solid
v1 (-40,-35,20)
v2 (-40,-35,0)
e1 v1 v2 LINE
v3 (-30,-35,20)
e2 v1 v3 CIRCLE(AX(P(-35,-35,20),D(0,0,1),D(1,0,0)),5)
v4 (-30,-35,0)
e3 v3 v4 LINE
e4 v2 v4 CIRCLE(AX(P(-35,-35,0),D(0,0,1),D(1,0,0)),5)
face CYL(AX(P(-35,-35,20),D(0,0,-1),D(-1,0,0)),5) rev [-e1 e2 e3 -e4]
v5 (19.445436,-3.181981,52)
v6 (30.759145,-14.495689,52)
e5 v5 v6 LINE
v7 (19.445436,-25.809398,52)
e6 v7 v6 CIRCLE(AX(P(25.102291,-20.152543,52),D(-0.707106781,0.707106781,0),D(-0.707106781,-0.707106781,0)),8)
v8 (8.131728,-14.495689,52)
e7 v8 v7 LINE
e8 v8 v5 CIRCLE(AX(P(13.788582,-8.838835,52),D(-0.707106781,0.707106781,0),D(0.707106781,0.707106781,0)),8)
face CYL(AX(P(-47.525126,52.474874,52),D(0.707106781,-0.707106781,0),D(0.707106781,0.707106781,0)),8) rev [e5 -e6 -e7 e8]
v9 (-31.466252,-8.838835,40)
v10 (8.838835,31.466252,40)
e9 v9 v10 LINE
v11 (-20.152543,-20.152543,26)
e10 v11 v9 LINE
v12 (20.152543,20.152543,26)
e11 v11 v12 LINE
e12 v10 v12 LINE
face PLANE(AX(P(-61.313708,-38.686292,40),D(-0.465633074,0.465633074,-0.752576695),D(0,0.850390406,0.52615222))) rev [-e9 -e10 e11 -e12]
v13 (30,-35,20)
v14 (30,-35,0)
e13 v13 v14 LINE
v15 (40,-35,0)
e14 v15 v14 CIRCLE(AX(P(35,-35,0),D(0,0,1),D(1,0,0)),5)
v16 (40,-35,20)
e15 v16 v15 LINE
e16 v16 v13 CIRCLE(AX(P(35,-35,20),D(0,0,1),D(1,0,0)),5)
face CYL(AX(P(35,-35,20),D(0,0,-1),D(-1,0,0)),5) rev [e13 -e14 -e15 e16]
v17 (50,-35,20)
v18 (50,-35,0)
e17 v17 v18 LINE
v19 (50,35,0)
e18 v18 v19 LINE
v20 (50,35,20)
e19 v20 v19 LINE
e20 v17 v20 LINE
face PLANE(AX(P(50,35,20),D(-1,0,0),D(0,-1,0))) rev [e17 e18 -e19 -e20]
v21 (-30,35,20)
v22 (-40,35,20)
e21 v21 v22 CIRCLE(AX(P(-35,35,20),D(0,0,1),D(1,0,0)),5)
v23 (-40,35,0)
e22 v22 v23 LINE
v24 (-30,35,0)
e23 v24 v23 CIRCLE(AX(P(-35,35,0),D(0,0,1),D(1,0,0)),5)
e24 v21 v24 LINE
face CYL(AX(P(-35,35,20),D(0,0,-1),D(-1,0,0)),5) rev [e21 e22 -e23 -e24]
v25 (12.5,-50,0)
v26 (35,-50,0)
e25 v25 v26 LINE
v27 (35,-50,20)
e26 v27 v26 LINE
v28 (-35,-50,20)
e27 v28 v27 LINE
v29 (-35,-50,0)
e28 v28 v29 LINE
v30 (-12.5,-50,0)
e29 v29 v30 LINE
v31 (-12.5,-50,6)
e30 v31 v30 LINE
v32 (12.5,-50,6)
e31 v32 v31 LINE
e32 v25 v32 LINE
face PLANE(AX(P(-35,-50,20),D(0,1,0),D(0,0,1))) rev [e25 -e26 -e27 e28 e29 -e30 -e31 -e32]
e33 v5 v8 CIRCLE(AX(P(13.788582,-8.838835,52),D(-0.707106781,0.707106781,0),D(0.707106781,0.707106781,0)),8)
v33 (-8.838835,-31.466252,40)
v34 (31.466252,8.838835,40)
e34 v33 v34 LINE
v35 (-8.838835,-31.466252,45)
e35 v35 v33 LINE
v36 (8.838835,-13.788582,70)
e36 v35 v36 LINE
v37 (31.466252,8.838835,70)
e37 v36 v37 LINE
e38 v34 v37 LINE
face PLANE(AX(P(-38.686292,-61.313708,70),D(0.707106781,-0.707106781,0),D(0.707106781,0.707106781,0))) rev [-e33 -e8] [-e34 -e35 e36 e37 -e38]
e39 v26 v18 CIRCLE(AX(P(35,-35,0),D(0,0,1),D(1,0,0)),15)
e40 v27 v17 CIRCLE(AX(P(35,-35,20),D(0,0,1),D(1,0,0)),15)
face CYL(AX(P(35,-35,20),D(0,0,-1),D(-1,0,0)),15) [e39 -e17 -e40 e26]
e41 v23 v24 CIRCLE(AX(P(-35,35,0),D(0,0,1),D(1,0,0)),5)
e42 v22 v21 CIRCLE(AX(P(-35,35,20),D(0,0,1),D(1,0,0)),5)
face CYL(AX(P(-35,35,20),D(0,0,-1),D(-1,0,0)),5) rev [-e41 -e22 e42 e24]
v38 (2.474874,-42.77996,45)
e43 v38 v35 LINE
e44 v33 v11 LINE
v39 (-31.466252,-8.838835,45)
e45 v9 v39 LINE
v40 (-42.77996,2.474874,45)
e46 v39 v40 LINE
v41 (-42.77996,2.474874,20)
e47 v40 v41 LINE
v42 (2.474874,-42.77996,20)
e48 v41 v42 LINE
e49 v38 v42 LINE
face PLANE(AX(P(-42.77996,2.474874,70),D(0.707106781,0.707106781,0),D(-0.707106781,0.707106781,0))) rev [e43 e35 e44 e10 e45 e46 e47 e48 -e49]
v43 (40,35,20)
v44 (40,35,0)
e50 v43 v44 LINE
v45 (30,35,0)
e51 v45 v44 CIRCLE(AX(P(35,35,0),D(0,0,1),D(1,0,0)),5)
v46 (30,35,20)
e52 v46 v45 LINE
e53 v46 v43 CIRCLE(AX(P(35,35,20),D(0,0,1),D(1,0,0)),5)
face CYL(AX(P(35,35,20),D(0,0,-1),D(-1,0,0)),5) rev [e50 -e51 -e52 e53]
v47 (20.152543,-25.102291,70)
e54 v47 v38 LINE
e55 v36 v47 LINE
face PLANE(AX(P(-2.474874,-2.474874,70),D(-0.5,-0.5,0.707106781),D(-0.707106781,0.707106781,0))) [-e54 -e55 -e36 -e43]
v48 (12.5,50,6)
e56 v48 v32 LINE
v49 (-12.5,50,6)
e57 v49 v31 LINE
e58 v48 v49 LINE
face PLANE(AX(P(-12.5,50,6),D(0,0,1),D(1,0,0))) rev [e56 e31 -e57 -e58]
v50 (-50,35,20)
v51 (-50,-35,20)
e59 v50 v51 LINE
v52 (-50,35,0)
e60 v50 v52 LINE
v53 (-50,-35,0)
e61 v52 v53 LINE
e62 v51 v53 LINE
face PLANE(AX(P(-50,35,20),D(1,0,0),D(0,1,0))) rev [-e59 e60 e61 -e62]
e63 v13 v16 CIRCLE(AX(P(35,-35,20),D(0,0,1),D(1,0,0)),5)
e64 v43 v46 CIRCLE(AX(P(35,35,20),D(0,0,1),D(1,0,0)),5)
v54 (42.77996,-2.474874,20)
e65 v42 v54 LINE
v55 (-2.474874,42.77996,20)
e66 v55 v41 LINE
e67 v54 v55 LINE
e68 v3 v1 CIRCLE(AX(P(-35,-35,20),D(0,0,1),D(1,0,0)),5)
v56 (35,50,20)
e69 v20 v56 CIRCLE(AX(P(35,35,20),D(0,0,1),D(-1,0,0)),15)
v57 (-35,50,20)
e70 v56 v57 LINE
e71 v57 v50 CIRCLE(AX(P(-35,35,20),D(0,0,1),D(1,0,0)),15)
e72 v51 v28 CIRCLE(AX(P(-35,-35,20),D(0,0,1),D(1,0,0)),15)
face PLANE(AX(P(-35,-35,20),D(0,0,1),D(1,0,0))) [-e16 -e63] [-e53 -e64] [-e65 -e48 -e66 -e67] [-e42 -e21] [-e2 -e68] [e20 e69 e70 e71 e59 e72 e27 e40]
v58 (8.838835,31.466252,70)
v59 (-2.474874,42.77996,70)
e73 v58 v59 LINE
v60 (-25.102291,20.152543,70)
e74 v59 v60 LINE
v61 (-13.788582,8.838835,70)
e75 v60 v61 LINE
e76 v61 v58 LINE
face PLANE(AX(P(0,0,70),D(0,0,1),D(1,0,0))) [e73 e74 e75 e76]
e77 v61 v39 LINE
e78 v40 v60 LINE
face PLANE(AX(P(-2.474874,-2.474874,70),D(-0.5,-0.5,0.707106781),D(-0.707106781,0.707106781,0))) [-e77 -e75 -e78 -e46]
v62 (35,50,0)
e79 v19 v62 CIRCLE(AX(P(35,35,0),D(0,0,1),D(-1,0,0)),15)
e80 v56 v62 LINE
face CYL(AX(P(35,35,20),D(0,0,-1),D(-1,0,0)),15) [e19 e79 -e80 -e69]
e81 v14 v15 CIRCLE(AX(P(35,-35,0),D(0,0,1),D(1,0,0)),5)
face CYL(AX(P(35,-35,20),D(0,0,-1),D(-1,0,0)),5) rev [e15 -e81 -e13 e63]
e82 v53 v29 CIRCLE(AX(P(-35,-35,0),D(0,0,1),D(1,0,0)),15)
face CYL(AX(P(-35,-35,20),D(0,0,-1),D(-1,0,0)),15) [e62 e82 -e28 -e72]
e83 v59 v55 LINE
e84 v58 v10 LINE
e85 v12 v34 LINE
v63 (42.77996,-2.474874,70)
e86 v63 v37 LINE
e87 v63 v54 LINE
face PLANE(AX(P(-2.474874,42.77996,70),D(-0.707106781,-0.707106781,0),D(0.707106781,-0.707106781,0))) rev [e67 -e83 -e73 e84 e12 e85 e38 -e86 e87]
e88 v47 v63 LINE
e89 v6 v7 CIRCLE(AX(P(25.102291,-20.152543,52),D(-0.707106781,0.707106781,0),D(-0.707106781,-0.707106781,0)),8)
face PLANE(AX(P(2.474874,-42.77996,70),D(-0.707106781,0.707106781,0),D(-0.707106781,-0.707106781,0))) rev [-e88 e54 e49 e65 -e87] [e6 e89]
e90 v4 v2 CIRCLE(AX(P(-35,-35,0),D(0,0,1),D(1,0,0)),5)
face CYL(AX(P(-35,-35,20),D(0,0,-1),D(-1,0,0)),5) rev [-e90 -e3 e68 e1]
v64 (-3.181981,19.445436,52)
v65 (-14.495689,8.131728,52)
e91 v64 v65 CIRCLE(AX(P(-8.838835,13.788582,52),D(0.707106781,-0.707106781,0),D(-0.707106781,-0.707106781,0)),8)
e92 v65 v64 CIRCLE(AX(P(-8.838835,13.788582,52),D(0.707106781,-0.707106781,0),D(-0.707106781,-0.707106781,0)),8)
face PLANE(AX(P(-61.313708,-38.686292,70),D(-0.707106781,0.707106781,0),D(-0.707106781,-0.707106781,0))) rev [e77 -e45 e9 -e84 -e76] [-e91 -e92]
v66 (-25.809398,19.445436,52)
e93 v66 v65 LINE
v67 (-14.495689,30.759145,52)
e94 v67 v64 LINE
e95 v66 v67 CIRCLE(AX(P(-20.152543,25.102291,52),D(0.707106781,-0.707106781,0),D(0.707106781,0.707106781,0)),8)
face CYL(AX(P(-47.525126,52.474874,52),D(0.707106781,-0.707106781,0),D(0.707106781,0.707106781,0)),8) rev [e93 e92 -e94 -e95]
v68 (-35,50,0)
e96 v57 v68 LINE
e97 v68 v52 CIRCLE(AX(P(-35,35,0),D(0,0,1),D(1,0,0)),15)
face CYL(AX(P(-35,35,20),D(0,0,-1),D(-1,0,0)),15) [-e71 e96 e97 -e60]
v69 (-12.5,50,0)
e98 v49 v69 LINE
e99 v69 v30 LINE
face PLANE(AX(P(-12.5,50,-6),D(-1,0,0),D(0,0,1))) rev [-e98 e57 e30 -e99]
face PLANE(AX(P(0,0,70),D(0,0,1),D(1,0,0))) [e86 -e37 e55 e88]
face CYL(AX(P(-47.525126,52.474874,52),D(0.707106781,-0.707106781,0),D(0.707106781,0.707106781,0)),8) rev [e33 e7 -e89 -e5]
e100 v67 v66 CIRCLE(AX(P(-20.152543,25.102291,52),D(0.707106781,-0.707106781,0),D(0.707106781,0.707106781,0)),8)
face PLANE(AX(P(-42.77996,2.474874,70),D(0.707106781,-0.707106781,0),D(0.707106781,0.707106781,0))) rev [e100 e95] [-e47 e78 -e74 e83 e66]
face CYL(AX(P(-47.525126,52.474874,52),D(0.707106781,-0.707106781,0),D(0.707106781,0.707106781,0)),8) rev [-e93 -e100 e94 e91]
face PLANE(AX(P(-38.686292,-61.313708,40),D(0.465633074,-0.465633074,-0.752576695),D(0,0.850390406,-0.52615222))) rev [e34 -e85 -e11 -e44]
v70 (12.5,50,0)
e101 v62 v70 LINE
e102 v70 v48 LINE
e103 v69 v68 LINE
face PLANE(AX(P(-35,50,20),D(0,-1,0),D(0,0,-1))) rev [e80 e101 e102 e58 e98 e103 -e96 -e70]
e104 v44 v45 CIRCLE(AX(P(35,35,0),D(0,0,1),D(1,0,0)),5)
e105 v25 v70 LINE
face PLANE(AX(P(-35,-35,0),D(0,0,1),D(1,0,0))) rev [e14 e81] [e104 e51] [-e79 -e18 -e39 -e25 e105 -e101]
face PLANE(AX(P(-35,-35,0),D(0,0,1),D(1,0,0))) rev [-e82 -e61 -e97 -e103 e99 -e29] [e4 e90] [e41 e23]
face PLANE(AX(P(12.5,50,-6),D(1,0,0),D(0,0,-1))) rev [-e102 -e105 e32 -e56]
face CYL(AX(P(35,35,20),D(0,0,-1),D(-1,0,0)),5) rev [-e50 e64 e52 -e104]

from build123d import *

# Parameters (mm, degrees)
BASE_PLATE_SKETCH_R       = 5
BASE_PLATE_DEPTH          = 20
PLATE_HOLES_12_DEPTH      = 114.578166916
PLATE_HOLES_12_DEPTH_BACK = 114.578166916
PLATE_HOLES_SKETCH_W      = 25
PLATE_HOLES_SKETCH_H      = 12
SQUARE_BOSS_DEPTH         = 50
BOSS_HOLE_16_DEPTH        = 125.295950858
BOSS_HOLE_16_DEPTH_BACK   = 125.295950858
BOSS_HOLE_SKETCH_R        = 8
BOSS_CHAMFER_25X45_SIZE   = 25
SLOT_CUT_DEPTH            = 122.4197622
SLOT_CUT_DEPTH_BACK       = 122.4197622


with BuildPart() as part:
    # Base Plate Sketch → Base Plate (new body)
    with BuildSketch(Plane.XY):
        with BuildLine():
            Line((-35, 50), (35, 50))
            ThreePointArc((35, 50), (45.606601718, 45.606601718), (50, 35))
            Line((50, 35), (50, -35))
            ThreePointArc((50, -35), (45.606601718, -45.606601718), (35, -50))
            Line((35, -50), (-35, -50))
            ThreePointArc((-35, -50), (-45.606601718, -45.606601718), (-50, -35))
            Line((-50, -35), (-50, 35))
            ThreePointArc((-50, 35), (-45.606601718, 45.606601718), (-35, 50))
        make_face()
        with Locations((-35, 35)):
            Circle(BASE_PLATE_SKETCH_R, mode=Mode.SUBTRACT)
        with Locations((35, 35)):
            Circle(BASE_PLATE_SKETCH_R, mode=Mode.SUBTRACT)
        with Locations((35, -35)):
            Circle(BASE_PLATE_SKETCH_R, mode=Mode.SUBTRACT)
        with Locations((-35, -35)):
            Circle(BASE_PLATE_SKETCH_R, mode=Mode.SUBTRACT)
    extrude(amount=BASE_PLATE_DEPTH)

    # Plate Holes Sketch → Plate Holes Ø12 (cut, two sides: drawn at the far end of the back side and taken through both)
    with BuildSketch(Plane.XZ.offset(50).offset(-PLATE_HOLES_12_DEPTH_BACK)):
        Rectangle(PLATE_HOLES_SKETCH_W, PLATE_HOLES_SKETCH_H)
    extrude(amount=PLATE_HOLES_12_DEPTH + PLATE_HOLES_12_DEPTH_BACK, mode=Mode.SUBTRACT)

    # Square Boss Sketch → Square Boss (add)
    with BuildSketch(Plane.XY.offset(20)):
        Polygon((-42.779960262, 2.474873734), (-2.474873734, 42.779960262), (42.779960262, -2.474873734), (2.474873734, -42.779960262), align=None)
    extrude(amount=SQUARE_BOSS_DEPTH)

    # Boss Hole Sketch → Boss Hole Ø16 (cut, two sides: drawn at the far end of the back side and taken through both)
    with BuildSketch(Plane(origin=(22.627416998, -22.627416998, 0), x_dir=(0, 0, -1), z_dir=(0.7071067811865462, -0.7071067811865488, 0)).offset(-BOSS_HOLE_16_DEPTH_BACK)):
        with Locations(Location((-52, 3.5, 0), (0, 0, 90))):
            Circle(BOSS_HOLE_SKETCH_R)
    extrude(amount=BOSS_HOLE_16_DEPTH + BOSS_HOLE_16_DEPTH_BACK, mode=Mode.SUBTRACT)

    # Boss Chamfer 25x45°
    boss_chamfer_25x45_edges = [part.edges().sort_by_distance(p)[0] for p in [
        (-20.152543264, -20.152543264, 70),
    ]]
    chamfer(boss_chamfer_25x45_edges, length=BOSS_CHAMFER_25X45_SIZE)

    # Slot Sketch → Slot Cut (cut, two sides: drawn at the far end of the back side and taken through both)
    with BuildSketch(Plane(origin=(20.152543264, 20.152543264, 0), x_dir=(0, 0, -1), z_dir=(0.7071067811865486, 0.7071067811865465, 0)).offset(-SLOT_CUT_DEPTH_BACK)):
        Polygon((-70, 16), (-40, 16), (-26, 0), (-40, -16), (-70, -16), align=None)
    extrude(amount=SLOT_CUT_DEPTH + SLOT_CUT_DEPTH_BACK, mode=Mode.SUBTRACT)


solid = part.part
